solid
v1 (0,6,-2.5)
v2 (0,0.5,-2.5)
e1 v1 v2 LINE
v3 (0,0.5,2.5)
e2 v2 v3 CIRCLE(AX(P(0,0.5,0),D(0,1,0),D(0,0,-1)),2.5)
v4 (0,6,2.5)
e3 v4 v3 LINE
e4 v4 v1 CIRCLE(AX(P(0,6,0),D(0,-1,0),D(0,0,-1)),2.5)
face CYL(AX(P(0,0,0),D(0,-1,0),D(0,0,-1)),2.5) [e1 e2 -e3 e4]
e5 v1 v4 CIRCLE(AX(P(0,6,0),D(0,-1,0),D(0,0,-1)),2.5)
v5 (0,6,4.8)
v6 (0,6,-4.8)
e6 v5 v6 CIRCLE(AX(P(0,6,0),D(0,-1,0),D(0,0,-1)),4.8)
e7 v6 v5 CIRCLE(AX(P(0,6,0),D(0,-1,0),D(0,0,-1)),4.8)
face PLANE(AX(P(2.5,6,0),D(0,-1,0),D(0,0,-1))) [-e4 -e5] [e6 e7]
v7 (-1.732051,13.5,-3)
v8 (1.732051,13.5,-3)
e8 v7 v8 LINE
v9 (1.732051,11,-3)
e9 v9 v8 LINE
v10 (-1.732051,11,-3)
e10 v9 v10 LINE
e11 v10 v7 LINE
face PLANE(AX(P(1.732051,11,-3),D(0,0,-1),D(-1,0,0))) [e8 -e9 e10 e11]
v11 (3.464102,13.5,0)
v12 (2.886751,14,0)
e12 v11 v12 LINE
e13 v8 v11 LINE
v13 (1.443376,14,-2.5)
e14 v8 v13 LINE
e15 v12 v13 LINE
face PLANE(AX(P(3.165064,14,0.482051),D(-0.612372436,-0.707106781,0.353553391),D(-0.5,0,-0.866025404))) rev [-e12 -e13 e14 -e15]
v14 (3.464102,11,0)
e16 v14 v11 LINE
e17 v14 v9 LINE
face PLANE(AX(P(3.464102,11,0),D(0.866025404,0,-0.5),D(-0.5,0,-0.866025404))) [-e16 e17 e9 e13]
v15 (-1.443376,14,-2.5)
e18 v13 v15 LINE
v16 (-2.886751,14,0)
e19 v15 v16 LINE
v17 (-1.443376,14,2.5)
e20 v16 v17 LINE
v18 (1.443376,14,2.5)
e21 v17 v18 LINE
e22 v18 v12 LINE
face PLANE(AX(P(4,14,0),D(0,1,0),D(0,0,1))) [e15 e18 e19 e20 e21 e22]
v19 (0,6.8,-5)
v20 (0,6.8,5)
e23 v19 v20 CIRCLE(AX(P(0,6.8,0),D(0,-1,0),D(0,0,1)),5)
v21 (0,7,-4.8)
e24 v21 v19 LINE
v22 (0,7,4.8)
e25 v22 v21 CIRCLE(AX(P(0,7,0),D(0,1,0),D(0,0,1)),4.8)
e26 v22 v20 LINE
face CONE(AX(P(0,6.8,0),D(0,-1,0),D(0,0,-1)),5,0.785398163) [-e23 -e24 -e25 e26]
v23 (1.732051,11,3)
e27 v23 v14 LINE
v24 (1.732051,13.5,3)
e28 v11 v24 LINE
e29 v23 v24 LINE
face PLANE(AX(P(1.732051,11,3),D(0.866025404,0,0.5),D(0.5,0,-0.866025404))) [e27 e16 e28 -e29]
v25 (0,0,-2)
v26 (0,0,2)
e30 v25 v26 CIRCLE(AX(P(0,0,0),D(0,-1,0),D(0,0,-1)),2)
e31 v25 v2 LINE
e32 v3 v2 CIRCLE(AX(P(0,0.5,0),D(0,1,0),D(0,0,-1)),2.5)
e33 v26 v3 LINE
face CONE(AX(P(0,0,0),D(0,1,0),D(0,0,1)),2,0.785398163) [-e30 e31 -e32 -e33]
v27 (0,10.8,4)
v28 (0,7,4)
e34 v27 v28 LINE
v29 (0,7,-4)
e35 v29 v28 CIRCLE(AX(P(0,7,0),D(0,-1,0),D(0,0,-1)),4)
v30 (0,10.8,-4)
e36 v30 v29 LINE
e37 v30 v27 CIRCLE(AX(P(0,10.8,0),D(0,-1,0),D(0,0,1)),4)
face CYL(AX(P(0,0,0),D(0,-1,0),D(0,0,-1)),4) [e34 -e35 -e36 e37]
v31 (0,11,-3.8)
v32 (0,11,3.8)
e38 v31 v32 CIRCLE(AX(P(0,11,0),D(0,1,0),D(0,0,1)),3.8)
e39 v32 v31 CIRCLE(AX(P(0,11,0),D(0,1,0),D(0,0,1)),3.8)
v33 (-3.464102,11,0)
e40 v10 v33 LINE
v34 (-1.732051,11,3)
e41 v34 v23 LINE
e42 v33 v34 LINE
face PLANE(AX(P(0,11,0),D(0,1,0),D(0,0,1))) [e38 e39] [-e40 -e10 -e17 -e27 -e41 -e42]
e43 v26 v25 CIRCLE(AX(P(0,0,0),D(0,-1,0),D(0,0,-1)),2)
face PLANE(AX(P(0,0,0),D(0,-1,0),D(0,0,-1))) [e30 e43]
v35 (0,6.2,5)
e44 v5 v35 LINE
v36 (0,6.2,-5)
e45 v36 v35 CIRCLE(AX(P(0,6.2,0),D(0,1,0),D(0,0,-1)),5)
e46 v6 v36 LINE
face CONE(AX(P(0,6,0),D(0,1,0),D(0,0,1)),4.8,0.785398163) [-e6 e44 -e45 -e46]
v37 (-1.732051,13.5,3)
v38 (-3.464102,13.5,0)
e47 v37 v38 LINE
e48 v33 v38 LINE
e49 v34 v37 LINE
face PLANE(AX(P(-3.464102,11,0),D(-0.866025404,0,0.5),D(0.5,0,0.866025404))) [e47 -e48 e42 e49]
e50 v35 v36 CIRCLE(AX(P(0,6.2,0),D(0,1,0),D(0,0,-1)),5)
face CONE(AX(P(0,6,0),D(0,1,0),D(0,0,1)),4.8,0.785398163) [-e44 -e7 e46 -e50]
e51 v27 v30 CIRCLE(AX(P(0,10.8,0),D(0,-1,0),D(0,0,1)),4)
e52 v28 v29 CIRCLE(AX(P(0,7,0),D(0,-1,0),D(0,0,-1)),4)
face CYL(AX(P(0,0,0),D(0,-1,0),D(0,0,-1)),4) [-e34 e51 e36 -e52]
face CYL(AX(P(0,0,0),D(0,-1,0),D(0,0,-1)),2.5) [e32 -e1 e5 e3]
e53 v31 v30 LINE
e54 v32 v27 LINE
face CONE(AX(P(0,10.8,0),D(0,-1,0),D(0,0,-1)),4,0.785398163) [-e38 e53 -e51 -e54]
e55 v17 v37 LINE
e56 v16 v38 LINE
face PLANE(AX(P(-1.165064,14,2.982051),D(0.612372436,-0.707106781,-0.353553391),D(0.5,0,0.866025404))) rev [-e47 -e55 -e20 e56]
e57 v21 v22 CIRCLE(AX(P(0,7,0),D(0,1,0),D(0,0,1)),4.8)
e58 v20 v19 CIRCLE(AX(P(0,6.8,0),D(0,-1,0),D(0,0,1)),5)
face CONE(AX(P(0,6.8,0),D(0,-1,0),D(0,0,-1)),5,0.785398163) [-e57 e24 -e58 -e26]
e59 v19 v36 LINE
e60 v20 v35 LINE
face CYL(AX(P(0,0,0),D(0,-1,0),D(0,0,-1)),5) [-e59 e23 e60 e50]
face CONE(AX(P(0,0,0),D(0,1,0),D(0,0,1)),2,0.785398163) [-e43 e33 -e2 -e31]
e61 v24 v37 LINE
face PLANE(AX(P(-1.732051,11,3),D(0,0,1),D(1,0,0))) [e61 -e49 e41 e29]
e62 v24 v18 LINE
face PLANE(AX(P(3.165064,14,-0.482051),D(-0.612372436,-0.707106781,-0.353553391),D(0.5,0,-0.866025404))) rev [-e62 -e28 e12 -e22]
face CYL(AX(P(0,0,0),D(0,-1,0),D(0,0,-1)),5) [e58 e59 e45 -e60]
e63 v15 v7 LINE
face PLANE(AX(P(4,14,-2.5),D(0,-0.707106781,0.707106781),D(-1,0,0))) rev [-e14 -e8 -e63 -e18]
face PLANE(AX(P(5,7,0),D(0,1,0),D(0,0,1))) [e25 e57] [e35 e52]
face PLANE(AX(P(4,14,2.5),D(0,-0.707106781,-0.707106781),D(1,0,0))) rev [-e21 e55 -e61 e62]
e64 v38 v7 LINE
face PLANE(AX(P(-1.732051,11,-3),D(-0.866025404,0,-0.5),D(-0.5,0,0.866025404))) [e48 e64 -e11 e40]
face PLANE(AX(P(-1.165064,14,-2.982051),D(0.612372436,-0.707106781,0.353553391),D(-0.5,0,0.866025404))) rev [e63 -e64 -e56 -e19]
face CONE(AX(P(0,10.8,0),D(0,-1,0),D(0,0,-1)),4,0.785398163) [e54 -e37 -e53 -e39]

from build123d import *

# Parameters (mm, degrees)
SKETCH4_OUTSIDE_W  = 15.98
SKETCH4_OUTSIDE_H  = 15.98
CUT_EXTRUDE2_DEPTH = 3
CHAMFER1_SIZE      = 0.5
CHAMFER2_SIZE      = 0.2


with BuildPart() as part:
    # Sketch2 → Revolve1 (revolve)
    with BuildSketch(Plane.XY, mode=Mode.PRIVATE) as revolve1_sk:
        Polygon((0, 0), (2.5, 0), (2.5, 6), (5, 6), (5, 7), (4, 7), (4, 14), (0, 14), align=None)
    revolve(revolve1_sk.sketch.rotate(Axis((0, 0, 0), (0, 1, 0)), 90), axis=Axis((0, 0, 0), (0, 1, 0)))

    # Sketch4 outside → Cut-Extrude2 (cut)
    with BuildSketch(Plane(origin=(0, 14, 0), x_dir=(1, 0, 0), z_dir=(0, 1, 0))):
        Rectangle(SKETCH4_OUTSIDE_W, SKETCH4_OUTSIDE_H)
        Polygon((1.732050808, 3), (-1.732050808, 3), (-3.464101615, 0), (-1.732050808, -3), (1.732050808, -3), (3.464101615, 0), align=None, mode=Mode.SUBTRACT)
    extrude(amount=-CUT_EXTRUDE2_DEPTH, mode=Mode.SUBTRACT)

    # Chamfer1
    chamfer1_edges = [part.edges().sort_by_distance(p)[0] for p in [
        (2.598076211, 14, -1.5),
        (2.598076211, 14, 1.5),
        (0, 14, 3),
        (-2.598076211, 14, 1.5),
        (-2.598076211, 14, -1.5),
        (0, 14, -3),
        (0, 0, 2.5),
    ]]
    chamfer(chamfer1_edges, length=CHAMFER1_SIZE)

    # Chamfer2
    chamfer2_edges = [part.edges().sort_by_distance(p)[0] for p in [
        (0, 11, 4),
        (0, 7, 5),
        (0, 6, 5),
    ]]
    chamfer(chamfer2_edges, length=CHAMFER2_SIZE)


solid = part.part
